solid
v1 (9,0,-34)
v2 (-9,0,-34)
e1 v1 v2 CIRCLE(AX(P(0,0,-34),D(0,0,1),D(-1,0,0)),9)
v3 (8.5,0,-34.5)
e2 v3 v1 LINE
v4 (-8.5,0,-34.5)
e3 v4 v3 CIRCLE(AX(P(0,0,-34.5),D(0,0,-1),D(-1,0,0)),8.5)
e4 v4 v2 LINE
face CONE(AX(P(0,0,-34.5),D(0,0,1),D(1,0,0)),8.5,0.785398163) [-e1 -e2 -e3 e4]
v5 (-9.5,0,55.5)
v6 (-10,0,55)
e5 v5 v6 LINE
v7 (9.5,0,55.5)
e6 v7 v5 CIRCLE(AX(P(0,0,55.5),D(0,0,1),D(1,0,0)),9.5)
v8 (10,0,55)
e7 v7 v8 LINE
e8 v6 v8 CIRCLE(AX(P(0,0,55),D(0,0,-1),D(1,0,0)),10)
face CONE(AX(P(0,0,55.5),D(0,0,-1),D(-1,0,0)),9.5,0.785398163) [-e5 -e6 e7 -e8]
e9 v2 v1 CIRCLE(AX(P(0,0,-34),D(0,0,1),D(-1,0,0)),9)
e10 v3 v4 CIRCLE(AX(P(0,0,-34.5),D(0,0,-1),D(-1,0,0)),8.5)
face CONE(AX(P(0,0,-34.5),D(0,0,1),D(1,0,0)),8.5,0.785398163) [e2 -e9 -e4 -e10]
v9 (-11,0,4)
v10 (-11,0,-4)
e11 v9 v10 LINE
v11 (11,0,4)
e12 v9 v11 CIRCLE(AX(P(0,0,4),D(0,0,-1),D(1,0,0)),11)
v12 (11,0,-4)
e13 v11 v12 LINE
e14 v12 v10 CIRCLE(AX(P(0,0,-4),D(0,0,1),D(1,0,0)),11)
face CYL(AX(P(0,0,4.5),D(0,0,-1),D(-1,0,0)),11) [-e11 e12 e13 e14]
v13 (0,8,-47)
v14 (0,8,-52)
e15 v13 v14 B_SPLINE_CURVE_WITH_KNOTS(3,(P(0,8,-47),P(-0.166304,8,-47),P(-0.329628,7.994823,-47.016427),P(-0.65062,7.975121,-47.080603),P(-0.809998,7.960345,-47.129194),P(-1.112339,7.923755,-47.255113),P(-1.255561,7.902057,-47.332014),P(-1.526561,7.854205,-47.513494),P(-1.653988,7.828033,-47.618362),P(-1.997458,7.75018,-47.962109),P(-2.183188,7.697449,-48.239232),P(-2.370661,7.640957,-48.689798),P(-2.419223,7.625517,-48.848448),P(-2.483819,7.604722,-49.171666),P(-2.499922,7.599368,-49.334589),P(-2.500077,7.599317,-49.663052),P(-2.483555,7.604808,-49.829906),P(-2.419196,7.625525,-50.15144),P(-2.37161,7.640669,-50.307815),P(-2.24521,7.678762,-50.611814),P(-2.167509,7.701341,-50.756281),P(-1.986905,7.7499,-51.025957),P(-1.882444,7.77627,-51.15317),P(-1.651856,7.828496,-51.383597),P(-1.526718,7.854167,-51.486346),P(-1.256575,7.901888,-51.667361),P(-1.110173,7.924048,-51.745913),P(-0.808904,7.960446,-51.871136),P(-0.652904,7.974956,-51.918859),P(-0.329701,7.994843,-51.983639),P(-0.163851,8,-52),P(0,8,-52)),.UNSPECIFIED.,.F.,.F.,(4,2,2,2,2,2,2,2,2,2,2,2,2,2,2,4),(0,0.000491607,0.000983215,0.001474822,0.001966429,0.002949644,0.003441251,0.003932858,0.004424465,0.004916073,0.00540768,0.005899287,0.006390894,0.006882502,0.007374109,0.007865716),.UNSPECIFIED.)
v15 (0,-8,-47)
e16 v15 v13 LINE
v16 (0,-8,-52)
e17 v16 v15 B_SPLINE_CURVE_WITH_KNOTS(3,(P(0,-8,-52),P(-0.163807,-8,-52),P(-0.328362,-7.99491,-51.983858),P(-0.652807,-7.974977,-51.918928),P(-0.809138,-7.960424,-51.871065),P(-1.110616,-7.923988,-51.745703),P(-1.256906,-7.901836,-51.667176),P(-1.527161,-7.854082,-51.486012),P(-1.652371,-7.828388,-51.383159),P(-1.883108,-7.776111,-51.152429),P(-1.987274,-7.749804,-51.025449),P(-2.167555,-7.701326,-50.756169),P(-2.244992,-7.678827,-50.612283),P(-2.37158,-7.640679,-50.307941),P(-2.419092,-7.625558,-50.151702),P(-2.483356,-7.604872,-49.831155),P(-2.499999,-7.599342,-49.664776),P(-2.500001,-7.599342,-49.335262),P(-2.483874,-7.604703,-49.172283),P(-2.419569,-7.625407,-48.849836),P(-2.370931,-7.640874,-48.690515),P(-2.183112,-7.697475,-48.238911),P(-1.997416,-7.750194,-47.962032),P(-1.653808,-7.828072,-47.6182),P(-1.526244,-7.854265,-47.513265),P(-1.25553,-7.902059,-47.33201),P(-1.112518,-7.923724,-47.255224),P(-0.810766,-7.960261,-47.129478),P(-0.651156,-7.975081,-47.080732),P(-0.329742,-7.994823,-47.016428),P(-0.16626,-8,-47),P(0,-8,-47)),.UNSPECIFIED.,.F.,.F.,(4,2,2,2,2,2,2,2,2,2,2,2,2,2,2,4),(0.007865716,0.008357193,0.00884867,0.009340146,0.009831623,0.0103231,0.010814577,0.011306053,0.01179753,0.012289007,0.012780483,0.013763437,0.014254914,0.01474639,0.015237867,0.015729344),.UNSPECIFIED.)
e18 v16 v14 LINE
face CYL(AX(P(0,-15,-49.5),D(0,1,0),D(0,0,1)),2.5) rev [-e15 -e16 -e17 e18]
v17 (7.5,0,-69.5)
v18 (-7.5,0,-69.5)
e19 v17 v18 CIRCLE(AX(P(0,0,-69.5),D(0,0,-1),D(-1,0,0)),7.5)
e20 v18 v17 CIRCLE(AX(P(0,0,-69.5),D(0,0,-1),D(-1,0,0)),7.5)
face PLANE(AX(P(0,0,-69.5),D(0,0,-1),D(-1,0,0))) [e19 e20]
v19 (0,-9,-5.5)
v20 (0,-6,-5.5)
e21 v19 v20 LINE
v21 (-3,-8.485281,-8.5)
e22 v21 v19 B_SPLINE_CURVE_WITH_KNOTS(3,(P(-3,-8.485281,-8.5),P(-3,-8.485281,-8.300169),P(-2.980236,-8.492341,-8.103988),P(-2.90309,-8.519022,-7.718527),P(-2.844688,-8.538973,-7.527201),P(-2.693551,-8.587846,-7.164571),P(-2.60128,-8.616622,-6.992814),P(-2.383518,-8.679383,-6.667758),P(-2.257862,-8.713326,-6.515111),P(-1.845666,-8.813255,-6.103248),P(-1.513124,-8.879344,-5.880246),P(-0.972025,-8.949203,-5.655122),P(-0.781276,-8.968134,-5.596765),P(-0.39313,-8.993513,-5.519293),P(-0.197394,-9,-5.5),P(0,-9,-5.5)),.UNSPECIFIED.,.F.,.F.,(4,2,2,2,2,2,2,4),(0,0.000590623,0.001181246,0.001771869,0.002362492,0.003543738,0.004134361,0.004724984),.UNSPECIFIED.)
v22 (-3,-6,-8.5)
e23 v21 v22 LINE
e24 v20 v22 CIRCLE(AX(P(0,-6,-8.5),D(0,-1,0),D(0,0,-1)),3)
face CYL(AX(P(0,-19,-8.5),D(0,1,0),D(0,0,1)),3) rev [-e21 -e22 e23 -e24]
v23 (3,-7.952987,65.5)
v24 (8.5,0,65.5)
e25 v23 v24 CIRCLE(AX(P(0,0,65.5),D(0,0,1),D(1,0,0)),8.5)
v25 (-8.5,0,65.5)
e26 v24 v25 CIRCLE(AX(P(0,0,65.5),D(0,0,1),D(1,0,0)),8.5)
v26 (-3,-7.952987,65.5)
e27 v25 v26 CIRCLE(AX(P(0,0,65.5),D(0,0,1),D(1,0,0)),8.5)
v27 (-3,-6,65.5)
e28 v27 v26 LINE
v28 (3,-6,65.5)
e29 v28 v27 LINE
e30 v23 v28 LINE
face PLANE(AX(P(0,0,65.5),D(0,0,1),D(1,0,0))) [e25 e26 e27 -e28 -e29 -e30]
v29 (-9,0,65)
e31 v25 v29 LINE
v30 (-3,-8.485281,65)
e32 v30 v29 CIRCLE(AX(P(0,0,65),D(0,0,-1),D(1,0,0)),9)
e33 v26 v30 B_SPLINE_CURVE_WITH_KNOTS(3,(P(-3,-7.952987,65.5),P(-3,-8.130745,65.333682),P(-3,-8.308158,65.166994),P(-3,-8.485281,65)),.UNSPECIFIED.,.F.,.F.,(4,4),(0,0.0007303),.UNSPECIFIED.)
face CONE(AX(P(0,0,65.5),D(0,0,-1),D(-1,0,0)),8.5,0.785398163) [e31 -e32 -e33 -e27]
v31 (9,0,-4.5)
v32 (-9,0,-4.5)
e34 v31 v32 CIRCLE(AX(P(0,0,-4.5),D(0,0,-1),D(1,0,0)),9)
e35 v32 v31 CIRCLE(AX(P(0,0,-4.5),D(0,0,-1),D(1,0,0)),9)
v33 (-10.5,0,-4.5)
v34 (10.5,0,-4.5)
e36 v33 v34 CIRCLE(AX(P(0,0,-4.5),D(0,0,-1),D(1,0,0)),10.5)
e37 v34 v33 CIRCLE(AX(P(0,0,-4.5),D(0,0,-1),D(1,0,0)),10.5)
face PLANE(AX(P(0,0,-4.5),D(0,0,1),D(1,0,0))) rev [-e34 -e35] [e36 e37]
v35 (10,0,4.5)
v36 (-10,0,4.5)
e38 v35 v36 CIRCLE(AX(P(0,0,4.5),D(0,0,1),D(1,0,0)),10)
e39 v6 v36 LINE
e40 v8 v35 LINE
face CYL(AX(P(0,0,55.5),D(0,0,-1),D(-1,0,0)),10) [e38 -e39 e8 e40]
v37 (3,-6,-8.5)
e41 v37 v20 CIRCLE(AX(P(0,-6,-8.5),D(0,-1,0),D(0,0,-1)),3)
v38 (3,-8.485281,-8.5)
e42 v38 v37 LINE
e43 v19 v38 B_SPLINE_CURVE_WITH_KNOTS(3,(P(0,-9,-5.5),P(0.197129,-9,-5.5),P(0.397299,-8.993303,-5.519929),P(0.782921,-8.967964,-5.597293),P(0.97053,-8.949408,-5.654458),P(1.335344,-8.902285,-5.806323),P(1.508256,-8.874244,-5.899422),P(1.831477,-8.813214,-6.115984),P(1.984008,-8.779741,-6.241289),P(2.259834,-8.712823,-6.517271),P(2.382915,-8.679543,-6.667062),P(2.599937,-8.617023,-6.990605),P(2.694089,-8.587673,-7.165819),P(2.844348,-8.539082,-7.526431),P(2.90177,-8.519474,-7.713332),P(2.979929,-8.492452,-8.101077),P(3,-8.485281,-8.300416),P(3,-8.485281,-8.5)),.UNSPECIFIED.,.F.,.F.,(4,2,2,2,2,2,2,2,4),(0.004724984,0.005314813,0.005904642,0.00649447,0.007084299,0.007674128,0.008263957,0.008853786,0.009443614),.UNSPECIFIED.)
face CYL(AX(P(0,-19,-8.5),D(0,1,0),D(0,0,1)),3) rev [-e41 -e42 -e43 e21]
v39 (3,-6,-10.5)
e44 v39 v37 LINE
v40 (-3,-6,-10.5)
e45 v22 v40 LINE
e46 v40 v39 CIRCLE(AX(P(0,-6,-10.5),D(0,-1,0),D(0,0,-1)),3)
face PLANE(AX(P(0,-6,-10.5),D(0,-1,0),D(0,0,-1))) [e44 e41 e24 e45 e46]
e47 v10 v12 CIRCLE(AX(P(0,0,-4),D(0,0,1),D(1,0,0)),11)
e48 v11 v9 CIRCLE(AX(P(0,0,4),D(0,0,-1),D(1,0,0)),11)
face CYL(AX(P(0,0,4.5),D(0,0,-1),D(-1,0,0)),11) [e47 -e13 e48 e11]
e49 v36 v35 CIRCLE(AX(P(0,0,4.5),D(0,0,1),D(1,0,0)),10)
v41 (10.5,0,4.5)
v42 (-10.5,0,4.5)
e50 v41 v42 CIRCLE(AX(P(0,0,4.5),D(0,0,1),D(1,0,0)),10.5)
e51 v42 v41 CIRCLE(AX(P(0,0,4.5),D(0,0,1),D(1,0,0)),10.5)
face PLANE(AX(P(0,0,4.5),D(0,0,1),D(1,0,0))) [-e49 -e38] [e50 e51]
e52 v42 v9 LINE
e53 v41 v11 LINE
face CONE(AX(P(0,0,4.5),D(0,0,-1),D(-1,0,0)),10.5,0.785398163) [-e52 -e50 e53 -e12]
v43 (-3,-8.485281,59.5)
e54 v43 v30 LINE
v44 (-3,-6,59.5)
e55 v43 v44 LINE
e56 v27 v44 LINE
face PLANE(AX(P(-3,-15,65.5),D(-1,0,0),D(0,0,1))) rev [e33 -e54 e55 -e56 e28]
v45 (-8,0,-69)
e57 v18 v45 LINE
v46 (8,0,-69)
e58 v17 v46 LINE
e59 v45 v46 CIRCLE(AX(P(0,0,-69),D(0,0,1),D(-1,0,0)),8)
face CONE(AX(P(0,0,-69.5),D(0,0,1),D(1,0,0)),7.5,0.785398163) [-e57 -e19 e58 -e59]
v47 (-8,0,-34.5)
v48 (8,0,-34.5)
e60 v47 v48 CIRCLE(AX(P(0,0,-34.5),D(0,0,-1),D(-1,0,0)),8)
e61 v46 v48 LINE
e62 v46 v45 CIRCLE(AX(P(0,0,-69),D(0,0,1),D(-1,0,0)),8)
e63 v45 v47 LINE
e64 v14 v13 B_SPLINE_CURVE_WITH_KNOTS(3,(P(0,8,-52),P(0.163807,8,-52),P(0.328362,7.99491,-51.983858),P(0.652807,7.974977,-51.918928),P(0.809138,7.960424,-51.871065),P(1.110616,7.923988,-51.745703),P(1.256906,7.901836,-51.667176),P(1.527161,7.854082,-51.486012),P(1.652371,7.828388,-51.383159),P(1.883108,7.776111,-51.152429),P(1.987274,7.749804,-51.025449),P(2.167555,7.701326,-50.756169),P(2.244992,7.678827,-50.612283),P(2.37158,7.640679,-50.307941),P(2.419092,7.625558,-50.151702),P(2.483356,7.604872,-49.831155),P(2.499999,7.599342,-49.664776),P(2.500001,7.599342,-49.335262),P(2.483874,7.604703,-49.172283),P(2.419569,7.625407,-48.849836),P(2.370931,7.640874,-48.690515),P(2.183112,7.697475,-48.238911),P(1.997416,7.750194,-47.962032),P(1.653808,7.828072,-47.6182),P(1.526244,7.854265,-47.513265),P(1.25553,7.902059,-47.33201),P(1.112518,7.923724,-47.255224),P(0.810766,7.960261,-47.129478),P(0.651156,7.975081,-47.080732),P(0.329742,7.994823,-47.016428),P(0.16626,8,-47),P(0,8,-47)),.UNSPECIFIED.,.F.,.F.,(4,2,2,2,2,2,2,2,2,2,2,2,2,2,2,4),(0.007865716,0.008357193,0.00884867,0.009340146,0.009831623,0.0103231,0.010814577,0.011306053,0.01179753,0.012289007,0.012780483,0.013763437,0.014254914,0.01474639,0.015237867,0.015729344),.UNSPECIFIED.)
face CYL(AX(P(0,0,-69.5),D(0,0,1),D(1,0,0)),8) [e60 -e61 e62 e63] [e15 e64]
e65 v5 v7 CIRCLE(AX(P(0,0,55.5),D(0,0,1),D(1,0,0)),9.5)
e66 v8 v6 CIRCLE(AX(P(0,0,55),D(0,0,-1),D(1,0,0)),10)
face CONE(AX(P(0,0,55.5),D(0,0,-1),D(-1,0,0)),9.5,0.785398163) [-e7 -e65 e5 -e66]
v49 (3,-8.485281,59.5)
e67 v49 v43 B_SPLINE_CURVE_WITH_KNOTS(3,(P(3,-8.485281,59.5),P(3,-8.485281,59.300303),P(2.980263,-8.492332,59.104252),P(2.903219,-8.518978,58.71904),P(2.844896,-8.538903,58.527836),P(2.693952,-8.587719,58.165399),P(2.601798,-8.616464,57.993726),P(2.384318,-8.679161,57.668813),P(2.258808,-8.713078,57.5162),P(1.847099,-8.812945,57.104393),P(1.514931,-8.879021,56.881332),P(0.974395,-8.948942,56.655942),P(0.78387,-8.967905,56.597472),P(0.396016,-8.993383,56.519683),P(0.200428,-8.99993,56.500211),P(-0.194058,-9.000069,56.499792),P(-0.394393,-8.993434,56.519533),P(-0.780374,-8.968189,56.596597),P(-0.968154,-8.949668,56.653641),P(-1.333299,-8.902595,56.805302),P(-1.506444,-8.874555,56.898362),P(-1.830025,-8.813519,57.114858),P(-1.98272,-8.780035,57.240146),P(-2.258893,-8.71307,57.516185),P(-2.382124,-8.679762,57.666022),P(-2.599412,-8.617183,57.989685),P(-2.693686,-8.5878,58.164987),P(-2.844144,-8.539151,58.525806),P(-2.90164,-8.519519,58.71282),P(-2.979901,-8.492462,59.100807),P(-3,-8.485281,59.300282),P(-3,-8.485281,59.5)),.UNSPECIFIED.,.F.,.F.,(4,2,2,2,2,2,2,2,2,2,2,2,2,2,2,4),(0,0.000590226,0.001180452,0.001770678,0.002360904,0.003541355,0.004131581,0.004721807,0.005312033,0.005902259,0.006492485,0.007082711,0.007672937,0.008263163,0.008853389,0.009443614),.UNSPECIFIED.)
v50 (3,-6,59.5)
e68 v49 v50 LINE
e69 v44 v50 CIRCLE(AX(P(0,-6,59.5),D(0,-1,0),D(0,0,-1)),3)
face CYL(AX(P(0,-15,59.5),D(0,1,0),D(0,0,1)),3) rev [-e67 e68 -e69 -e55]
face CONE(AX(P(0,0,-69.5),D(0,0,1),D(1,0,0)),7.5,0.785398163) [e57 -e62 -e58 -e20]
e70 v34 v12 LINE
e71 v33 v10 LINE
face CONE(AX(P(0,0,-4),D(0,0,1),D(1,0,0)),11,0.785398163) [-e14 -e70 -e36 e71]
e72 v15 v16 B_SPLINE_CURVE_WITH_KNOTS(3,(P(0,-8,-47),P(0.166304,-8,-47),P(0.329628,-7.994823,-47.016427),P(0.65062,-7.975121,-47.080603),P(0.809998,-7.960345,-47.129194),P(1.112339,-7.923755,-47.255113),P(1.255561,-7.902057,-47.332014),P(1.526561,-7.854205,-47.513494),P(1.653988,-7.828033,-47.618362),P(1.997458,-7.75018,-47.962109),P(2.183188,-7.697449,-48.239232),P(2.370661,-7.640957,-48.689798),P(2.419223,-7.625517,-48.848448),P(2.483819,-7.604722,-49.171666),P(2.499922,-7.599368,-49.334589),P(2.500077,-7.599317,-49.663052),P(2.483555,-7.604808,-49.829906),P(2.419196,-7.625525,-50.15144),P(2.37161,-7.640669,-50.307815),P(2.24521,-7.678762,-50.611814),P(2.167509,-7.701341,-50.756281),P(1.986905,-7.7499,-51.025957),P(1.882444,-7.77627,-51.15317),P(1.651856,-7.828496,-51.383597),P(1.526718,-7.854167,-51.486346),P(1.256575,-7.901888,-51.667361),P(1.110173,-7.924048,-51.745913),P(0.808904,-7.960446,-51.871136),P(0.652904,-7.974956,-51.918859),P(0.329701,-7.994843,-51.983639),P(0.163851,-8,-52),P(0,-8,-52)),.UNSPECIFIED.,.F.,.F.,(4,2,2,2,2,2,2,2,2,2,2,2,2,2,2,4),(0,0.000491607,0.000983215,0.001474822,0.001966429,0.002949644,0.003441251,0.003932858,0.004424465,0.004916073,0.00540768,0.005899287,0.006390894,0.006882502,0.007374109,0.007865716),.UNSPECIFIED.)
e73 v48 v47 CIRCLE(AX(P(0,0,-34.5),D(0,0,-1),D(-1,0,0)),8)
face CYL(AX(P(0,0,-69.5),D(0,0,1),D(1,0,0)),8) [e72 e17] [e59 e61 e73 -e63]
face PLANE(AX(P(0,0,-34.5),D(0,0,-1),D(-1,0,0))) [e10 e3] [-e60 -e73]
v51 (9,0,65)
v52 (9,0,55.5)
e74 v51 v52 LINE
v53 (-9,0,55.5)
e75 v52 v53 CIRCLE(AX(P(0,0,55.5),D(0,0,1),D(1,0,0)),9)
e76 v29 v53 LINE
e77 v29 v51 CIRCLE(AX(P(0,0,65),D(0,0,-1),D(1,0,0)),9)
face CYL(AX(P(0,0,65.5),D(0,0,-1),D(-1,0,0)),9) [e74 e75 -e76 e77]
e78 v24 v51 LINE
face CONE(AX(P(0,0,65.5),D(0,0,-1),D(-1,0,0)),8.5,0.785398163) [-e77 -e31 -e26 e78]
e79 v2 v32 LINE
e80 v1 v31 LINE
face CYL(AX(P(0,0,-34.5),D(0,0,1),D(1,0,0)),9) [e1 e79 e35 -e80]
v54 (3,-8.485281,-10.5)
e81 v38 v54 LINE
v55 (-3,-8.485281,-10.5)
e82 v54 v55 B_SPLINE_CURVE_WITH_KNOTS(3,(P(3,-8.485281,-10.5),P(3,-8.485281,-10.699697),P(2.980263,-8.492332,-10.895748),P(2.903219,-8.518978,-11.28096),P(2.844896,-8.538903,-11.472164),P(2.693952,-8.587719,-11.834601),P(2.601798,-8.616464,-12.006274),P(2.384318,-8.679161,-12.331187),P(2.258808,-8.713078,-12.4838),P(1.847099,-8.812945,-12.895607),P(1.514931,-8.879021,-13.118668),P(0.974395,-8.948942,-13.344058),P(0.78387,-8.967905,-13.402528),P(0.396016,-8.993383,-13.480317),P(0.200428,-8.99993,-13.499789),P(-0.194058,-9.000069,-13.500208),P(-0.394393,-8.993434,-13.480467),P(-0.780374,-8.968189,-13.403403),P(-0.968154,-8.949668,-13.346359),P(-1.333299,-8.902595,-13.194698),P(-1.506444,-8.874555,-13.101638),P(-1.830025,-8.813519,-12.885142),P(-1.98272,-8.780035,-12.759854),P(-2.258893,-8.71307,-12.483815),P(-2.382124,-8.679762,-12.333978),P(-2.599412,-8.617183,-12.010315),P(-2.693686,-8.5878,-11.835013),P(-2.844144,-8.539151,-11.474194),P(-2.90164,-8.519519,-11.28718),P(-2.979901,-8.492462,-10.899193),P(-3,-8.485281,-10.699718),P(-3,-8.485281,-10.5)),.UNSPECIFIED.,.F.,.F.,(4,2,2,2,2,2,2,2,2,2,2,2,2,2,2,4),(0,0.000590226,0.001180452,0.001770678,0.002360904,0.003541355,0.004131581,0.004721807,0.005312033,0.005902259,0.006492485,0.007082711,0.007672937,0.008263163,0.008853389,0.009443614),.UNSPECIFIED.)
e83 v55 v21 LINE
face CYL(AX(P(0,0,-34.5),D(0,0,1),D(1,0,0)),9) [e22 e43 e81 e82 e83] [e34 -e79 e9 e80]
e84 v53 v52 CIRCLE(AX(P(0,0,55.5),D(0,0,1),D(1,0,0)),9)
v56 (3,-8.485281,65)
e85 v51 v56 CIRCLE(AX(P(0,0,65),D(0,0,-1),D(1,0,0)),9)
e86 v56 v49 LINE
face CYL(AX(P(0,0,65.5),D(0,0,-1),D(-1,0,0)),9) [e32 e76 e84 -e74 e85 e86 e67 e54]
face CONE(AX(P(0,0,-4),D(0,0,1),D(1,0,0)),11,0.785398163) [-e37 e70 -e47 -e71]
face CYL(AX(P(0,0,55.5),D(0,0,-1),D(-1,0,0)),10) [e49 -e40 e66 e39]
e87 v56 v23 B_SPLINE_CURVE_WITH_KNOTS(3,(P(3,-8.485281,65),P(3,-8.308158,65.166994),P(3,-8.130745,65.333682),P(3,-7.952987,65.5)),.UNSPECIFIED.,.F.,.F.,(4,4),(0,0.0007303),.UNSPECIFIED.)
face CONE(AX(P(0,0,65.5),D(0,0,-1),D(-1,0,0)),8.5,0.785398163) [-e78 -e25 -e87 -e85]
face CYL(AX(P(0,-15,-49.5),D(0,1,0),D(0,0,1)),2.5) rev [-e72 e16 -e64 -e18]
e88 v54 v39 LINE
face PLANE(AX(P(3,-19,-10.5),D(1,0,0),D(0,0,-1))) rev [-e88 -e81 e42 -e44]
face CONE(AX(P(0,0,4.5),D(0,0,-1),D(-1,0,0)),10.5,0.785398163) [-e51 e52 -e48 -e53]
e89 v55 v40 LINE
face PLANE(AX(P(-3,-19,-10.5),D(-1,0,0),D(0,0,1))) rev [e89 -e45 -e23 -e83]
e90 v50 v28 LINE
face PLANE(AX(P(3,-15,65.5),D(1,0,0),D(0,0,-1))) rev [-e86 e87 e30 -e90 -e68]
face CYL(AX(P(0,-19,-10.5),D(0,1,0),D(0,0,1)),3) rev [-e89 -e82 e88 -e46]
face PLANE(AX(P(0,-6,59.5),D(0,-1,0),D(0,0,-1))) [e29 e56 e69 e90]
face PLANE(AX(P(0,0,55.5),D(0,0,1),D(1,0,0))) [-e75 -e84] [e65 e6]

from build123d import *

# Parameters (mm, degrees)
SKETCH1_R           = 11
BOSS_EXTRUDE1_DEPTH = 4.5
SKETCH2_R           = 9
BOSS_EXTRUDE2_DEPTH = 30
SKETCH3_R           = 10
BOSS_EXTRUDE3_DEPTH = 51
BOSS_EXTRUDE4_START = 10
SKETCH4_R           = 9
BOSS_EXTRUDE4_DEPTH = 10
CUT_EXTRUDE1_DEPTH  = 15
BOSS_EXTRUDE5_DEPTH = 6
CUT_EXTRUDE2_DEPTH  = 19
BOSS_EXTRUDE6_DEPTH = 6
CHAMFER1_SIZE       = 0.5
SKETCH9_R           = 8
BOSS_EXTRUDE7_DEPTH = 35
CHAMFER2_SIZE       = 0.5
SKETCH10_R          = 2.5
CUT_EXTRUDE3_DEPTH  = 15


with BuildPart() as part:
    # Sketch1 → Boss-Extrude1 (new, symmetric)
    with BuildSketch(Plane.XY):
        Circle(SKETCH1_R)
    extrude(amount=BOSS_EXTRUDE1_DEPTH, both=True)

    # Sketch2 → Boss-Extrude2 (add)
    with BuildSketch(Plane(origin=(0, 0, -4.5), x_dir=(-1, 0, 0), z_dir=(0, 0, -1))):
        with Locations(Location((0, 0, 0), (0, 0, 180))):
            Circle(SKETCH2_R)
    extrude(amount=BOSS_EXTRUDE2_DEPTH)

    # Sketch3 → Boss-Extrude3 (add)
    with BuildSketch(Plane.XY.offset(4.5)):
        Circle(SKETCH3_R)
    extrude(amount=BOSS_EXTRUDE3_DEPTH)

    # Sketch4 → Boss-Extrude4 (add)
    with BuildSketch(Plane.XY.offset(55.5).offset(BOSS_EXTRUDE4_START)):
        Circle(SKETCH4_R)
    extrude(amount=-BOSS_EXTRUDE4_DEPTH)

    # Sketch5 → Cut-Extrude1 (cut)
    with BuildSketch(Plane(origin=(0, 0, 0), x_dir=(1, 0, 0), z_dir=(0, 1, 0))):
        with BuildLine():
            Line((-3, -65.5), (-3, -59.5))
            ThreePointArc((-3, -59.5), (0, -56.5), (3, -59.5))
            Line((3, -59.5), (3, -65.5))
            ThreePointArc((3, -65.5), (0, -68.5), (-3, -65.5))
        make_face()
    extrude(amount=-CUT_EXTRUDE1_DEPTH, mode=Mode.SUBTRACT)

    # Sketch6 → Boss-Extrude5 (add)
    with BuildSketch(Plane.XZ):
        with BuildLine():
            Line((3, 65.5), (-3, 65.5))
            Line((-3, 65.5), (-3, 59.5))
            ThreePointArc((-3, 59.5), (0, 56.5), (3, 59.5))
            Line((3, 59.5), (3, 65.5))
        make_face()
    extrude(amount=BOSS_EXTRUDE5_DEPTH)

    # Sketch7 → Cut-Extrude2 (cut)
    with BuildSketch(Plane(origin=(0, 0, 0), x_dir=(1, 0, 0), z_dir=(0, 1, 0))):
        with BuildLine():
            Line((3, 10.5), (3, 8.5))
            ThreePointArc((3, 8.5), (0, 5.5), (-3, 8.5))
            Line((-3, 8.5), (-3, 10.5))
            ThreePointArc((-3, 10.5), (0, 13.5), (3, 10.5))
        make_face()
    extrude(amount=-CUT_EXTRUDE2_DEPTH, mode=Mode.SUBTRACT)

    # Sketch8 → Boss-Extrude6 (add)
    with BuildSketch(Plane.XZ):
        with BuildLine():
            Line((3, -10.5), (3, -8.5))
            ThreePointArc((3, -8.5), (0, -5.5), (-3, -8.5))
            Line((-3, -8.5), (-3, -10.5))
            ThreePointArc((-3, -10.5), (0, -13.5), (3, -10.5))
        make_face()
    extrude(amount=BOSS_EXTRUDE6_DEPTH)

    # Chamfer1
    chamfer1_edges = [part.edges().sort_by_distance(p)[0] for p in [
        (-10, 0, 55.5),
        (-5.196152423, 7.348469228, 65.5),
        (-11, 0, -4.5),
        (-11, 0, 4.5),
        (-9, 0, -34.5),
    ]]
    chamfer(chamfer1_edges, length=CHAMFER1_SIZE)

    # Sketch9 → Boss-Extrude7 (add)
    with BuildSketch(Plane(origin=(0, 0, -34.5), x_dir=(-1, 0, 0), z_dir=(0, 0, -1))):
        Circle(SKETCH9_R)
    extrude(amount=BOSS_EXTRUDE7_DEPTH)

    # Chamfer2
    chamfer2_edges = [part.edges().sort_by_distance(p)[0] for p in [
        (8, 0, -69.5),
    ]]
    chamfer(chamfer2_edges, length=CHAMFER2_SIZE)

    # Sketch10 → Cut-Extrude3 (cut, symmetric)
    with BuildSketch(Plane(origin=(0, 0, 0), x_dir=(1, 0, 0), z_dir=(0, 1, 0))):
        with Locations(Location((0, 49.5, 0), (0, 0, 270))):
            Circle(SKETCH10_R)
    extrude(amount=CUT_EXTRUDE3_DEPTH, both=True, mode=Mode.SUBTRACT)


solid = part.part
